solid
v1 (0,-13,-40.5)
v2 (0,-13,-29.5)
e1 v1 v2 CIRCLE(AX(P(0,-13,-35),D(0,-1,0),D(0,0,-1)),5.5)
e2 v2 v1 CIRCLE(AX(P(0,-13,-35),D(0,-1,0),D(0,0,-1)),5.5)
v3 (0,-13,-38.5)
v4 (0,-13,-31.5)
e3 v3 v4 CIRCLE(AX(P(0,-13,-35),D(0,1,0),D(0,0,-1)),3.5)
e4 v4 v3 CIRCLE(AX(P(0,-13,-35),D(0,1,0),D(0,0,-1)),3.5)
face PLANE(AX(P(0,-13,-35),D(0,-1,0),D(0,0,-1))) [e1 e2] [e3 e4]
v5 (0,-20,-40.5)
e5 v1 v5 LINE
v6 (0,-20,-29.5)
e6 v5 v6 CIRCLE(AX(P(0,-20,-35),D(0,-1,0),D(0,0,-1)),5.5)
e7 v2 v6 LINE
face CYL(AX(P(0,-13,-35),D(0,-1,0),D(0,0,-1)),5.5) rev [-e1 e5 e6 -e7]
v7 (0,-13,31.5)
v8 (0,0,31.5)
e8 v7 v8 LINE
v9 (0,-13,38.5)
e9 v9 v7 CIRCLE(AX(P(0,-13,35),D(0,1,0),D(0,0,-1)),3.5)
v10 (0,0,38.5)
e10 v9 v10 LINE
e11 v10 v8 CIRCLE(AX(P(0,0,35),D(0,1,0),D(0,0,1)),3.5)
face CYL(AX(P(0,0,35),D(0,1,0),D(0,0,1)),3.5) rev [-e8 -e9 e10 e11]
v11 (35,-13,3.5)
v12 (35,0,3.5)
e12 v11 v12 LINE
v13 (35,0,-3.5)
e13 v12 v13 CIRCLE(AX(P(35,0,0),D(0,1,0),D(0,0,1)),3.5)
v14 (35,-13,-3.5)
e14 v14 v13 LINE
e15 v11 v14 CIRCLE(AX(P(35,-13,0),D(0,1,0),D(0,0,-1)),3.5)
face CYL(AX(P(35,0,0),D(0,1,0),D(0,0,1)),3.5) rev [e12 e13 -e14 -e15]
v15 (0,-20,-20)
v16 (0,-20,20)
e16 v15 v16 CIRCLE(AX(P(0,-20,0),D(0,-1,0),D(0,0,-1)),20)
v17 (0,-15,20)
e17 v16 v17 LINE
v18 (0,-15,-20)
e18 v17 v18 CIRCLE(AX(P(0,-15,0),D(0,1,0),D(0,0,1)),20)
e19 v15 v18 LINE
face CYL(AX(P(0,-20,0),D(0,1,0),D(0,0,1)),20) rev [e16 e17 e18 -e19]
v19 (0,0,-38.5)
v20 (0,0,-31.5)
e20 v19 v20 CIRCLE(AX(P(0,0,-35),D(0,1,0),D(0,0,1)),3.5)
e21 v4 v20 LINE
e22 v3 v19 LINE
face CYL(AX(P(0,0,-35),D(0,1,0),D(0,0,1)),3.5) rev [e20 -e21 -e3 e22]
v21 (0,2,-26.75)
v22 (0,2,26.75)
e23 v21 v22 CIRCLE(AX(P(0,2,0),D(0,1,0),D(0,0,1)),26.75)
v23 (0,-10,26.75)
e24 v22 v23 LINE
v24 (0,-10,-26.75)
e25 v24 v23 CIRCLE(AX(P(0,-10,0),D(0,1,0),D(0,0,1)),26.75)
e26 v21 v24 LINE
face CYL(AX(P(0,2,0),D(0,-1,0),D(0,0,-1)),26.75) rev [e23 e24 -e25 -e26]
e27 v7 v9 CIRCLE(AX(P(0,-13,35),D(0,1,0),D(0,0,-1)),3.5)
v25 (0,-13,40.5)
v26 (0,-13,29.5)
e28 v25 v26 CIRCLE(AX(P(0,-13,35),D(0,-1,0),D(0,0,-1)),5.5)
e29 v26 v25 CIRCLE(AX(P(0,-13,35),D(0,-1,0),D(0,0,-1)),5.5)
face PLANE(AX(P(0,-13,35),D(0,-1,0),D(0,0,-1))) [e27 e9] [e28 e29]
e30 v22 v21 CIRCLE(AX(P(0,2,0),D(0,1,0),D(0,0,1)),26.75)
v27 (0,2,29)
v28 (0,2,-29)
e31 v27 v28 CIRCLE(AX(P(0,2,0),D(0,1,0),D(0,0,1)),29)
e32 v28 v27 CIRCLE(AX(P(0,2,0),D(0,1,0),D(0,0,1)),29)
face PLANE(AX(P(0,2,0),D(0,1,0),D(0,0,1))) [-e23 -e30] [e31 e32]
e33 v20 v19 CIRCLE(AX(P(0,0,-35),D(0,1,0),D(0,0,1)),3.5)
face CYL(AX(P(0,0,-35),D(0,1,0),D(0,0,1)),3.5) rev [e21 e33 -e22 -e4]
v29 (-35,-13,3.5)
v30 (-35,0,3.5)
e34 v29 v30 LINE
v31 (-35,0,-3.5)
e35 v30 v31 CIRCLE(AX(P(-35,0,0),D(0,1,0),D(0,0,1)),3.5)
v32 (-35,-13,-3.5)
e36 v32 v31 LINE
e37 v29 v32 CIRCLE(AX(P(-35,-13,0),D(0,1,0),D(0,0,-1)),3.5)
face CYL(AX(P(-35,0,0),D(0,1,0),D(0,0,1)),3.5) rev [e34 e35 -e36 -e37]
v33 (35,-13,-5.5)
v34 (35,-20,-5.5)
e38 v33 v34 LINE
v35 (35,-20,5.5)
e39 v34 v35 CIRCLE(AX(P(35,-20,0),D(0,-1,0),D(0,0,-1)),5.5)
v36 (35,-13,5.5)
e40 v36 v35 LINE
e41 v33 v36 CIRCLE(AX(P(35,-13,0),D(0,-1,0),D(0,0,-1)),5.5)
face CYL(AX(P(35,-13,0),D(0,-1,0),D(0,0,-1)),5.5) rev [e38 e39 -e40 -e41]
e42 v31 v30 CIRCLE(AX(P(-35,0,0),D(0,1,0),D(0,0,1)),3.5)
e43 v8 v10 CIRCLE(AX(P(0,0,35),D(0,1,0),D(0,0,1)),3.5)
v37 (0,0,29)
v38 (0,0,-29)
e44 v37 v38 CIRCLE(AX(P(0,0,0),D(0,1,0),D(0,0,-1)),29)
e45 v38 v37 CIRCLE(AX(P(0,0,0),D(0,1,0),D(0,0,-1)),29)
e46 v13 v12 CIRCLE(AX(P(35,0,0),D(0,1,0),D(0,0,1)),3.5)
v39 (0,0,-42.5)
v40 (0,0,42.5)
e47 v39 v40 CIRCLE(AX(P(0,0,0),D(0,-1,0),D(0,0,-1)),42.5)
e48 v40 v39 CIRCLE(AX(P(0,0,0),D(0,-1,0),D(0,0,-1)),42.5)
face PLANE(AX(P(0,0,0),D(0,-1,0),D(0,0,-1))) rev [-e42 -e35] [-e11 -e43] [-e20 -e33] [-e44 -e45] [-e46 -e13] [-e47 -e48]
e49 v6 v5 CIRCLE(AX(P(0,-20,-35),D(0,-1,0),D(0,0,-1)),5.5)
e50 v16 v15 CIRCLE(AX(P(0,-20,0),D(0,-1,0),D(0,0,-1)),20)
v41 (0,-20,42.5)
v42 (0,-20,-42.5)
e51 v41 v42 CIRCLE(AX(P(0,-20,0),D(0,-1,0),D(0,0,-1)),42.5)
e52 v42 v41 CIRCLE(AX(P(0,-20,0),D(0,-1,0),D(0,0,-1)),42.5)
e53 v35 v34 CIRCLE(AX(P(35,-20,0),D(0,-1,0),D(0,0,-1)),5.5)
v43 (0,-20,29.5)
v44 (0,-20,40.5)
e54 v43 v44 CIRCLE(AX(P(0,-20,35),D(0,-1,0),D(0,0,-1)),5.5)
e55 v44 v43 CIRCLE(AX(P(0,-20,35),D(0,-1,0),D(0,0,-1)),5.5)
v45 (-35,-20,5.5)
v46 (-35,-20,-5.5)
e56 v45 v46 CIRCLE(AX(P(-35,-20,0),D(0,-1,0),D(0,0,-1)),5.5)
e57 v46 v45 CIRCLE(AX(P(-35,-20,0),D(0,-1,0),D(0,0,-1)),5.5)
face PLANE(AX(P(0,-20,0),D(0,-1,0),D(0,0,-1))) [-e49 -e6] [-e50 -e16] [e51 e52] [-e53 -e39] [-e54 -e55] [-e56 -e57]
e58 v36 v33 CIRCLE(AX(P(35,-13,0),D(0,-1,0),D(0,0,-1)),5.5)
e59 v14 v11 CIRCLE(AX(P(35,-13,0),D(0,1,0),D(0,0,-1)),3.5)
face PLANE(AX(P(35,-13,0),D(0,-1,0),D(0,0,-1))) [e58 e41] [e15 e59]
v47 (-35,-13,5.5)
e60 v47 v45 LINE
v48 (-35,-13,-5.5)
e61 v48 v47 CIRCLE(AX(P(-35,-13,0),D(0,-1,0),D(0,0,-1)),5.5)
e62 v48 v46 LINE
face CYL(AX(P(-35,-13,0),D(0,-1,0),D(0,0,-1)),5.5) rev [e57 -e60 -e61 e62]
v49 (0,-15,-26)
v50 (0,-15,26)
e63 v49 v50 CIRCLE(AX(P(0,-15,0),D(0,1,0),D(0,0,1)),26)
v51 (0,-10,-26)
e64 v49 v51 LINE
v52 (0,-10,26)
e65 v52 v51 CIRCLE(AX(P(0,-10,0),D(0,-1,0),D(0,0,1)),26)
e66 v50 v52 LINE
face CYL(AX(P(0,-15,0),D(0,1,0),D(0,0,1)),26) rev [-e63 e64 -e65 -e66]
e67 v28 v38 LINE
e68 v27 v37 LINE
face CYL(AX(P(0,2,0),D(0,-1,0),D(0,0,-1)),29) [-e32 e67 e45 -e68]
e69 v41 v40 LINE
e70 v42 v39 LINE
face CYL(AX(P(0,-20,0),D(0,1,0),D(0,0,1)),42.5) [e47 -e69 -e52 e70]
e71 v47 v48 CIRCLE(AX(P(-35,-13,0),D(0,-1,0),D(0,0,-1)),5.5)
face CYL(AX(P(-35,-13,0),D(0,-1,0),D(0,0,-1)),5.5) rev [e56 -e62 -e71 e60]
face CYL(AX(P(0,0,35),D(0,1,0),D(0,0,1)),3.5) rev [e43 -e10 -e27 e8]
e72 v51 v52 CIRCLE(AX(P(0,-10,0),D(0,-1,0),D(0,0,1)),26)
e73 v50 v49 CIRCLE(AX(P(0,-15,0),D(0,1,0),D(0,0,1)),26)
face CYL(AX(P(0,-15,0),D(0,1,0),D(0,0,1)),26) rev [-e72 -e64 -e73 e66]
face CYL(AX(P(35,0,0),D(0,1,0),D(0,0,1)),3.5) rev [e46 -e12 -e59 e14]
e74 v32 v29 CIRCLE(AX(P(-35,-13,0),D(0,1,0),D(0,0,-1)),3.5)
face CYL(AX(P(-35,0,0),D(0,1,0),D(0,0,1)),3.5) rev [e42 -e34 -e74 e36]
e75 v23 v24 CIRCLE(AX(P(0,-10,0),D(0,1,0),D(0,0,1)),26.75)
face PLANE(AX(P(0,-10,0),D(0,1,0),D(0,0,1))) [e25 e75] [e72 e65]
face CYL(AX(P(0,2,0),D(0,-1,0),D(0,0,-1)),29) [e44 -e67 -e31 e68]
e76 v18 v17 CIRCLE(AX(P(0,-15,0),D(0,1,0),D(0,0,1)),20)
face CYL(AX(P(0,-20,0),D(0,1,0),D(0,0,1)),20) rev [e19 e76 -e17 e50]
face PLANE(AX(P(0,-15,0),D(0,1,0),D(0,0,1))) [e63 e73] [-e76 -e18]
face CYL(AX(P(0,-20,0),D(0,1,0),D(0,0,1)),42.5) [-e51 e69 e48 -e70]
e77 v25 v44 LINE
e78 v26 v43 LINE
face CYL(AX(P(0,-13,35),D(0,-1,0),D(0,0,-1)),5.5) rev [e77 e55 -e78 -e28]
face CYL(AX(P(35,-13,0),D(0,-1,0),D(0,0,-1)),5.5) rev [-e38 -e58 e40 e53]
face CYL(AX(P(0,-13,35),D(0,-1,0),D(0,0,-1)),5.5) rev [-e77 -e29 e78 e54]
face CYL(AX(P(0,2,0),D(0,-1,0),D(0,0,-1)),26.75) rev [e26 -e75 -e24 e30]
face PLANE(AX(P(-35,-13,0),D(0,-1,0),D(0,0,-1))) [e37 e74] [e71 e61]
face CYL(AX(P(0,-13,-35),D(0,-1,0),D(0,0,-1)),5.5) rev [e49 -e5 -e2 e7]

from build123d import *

# Parameters (mm, degrees)
SKETCH1_R            = 42.5
SKETCH1_R_2          = 20
BOSS_EXTRUDE1_DEPTH  = 20
M6_CLEARANCE_HOLE1_D = 7
SKETCH4_R            = 26
CUT_EXTRUDE1_DEPTH   = 15
SKETCH5_R            = 29
SKETCH5_R_2          = 26.75
BOSS_EXTRUDE3_DEPTH  = 2
CUT_EXTRUDE2_START   = -12
SKETCH6_R            = 26.75
CUT_EXTRUDE2_DEPTH   = 12
SKETCH7_R            = 5.5
CUT_EXTRUDE3_DEPTH   = 7


with BuildPart() as part:
    # Sketch1 → Boss-Extrude1 (new body)
    with BuildSketch(Plane.XZ):
        with Locations(Location((0, 0, 0), (0, 0, 270))):
            Circle(SKETCH1_R)
        with Locations(Location((0, 0, 0), (0, 0, 270))):
            Circle(SKETCH1_R_2, mode=Mode.SUBTRACT)
    extrude(amount=BOSS_EXTRUDE1_DEPTH)

    # M6 Clearance Hole1 (through all)
    with Locations(Plane(origin=(0, 0, 0), x_dir=(1, 0, 0), z_dir=(0, 1, 0))):
        with Locations((0, -35), (0, 35), (-35, 0), (35, 0)):
            Hole(M6_CLEARANCE_HOLE1_D / 2)

    # Sketch4 → Cut-Extrude1 (cut)
    with BuildSketch(Plane(origin=(0, 0, 0), x_dir=(1, 0, 0), z_dir=(0, 1, 0))):
        with Locations(Location((0, 0, 0), (0, 0, 270))):
            Circle(SKETCH4_R)
    extrude(amount=-CUT_EXTRUDE1_DEPTH, mode=Mode.SUBTRACT)

    # Sketch5 → Boss-Extrude3 (add)
    with BuildSketch(Plane(origin=(0, 0, 0), x_dir=(1, 0, 0), z_dir=(0, 1, 0))):
        with Locations(Location((0, 0, 0), (0, 0, 90))):
            Circle(SKETCH5_R)
        with Locations(Location((0, 0, 0), (0, 0, 270))):
            Circle(SKETCH5_R_2, mode=Mode.SUBTRACT)
    extrude(amount=BOSS_EXTRUDE3_DEPTH)

    # Sketch6 → Cut-Extrude2 (cut)
    with BuildSketch(Plane(origin=(0, 2, 0), x_dir=(1, 0, 0), z_dir=(0, 1, 0)).offset(CUT_EXTRUDE2_START)):
        with Locations(Location((0, 0, 0), (0, 0, 270))):
            Circle(SKETCH6_R)
    extrude(amount=CUT_EXTRUDE2_DEPTH, mode=Mode.SUBTRACT)

    # Sketch7 → Cut-Extrude3 (cut)
    with BuildSketch(Plane.XZ.offset(20)):
        with Locations(Location((0, 35, 0), (0, 0, 270))):
            Circle(SKETCH7_R)
        with Locations(Location((-35, 0, 0), (0, 0, 270))):
            Circle(SKETCH7_R)
        with Locations(Location((0, -35, 0), (0, 0, 270))):
            Circle(SKETCH7_R)
        with Locations(Location((35, 0, 0), (0, 0, 270))):
            Circle(SKETCH7_R)
    extrude(amount=-CUT_EXTRUDE3_DEPTH, mode=Mode.SUBTRACT)


solid = part.part
